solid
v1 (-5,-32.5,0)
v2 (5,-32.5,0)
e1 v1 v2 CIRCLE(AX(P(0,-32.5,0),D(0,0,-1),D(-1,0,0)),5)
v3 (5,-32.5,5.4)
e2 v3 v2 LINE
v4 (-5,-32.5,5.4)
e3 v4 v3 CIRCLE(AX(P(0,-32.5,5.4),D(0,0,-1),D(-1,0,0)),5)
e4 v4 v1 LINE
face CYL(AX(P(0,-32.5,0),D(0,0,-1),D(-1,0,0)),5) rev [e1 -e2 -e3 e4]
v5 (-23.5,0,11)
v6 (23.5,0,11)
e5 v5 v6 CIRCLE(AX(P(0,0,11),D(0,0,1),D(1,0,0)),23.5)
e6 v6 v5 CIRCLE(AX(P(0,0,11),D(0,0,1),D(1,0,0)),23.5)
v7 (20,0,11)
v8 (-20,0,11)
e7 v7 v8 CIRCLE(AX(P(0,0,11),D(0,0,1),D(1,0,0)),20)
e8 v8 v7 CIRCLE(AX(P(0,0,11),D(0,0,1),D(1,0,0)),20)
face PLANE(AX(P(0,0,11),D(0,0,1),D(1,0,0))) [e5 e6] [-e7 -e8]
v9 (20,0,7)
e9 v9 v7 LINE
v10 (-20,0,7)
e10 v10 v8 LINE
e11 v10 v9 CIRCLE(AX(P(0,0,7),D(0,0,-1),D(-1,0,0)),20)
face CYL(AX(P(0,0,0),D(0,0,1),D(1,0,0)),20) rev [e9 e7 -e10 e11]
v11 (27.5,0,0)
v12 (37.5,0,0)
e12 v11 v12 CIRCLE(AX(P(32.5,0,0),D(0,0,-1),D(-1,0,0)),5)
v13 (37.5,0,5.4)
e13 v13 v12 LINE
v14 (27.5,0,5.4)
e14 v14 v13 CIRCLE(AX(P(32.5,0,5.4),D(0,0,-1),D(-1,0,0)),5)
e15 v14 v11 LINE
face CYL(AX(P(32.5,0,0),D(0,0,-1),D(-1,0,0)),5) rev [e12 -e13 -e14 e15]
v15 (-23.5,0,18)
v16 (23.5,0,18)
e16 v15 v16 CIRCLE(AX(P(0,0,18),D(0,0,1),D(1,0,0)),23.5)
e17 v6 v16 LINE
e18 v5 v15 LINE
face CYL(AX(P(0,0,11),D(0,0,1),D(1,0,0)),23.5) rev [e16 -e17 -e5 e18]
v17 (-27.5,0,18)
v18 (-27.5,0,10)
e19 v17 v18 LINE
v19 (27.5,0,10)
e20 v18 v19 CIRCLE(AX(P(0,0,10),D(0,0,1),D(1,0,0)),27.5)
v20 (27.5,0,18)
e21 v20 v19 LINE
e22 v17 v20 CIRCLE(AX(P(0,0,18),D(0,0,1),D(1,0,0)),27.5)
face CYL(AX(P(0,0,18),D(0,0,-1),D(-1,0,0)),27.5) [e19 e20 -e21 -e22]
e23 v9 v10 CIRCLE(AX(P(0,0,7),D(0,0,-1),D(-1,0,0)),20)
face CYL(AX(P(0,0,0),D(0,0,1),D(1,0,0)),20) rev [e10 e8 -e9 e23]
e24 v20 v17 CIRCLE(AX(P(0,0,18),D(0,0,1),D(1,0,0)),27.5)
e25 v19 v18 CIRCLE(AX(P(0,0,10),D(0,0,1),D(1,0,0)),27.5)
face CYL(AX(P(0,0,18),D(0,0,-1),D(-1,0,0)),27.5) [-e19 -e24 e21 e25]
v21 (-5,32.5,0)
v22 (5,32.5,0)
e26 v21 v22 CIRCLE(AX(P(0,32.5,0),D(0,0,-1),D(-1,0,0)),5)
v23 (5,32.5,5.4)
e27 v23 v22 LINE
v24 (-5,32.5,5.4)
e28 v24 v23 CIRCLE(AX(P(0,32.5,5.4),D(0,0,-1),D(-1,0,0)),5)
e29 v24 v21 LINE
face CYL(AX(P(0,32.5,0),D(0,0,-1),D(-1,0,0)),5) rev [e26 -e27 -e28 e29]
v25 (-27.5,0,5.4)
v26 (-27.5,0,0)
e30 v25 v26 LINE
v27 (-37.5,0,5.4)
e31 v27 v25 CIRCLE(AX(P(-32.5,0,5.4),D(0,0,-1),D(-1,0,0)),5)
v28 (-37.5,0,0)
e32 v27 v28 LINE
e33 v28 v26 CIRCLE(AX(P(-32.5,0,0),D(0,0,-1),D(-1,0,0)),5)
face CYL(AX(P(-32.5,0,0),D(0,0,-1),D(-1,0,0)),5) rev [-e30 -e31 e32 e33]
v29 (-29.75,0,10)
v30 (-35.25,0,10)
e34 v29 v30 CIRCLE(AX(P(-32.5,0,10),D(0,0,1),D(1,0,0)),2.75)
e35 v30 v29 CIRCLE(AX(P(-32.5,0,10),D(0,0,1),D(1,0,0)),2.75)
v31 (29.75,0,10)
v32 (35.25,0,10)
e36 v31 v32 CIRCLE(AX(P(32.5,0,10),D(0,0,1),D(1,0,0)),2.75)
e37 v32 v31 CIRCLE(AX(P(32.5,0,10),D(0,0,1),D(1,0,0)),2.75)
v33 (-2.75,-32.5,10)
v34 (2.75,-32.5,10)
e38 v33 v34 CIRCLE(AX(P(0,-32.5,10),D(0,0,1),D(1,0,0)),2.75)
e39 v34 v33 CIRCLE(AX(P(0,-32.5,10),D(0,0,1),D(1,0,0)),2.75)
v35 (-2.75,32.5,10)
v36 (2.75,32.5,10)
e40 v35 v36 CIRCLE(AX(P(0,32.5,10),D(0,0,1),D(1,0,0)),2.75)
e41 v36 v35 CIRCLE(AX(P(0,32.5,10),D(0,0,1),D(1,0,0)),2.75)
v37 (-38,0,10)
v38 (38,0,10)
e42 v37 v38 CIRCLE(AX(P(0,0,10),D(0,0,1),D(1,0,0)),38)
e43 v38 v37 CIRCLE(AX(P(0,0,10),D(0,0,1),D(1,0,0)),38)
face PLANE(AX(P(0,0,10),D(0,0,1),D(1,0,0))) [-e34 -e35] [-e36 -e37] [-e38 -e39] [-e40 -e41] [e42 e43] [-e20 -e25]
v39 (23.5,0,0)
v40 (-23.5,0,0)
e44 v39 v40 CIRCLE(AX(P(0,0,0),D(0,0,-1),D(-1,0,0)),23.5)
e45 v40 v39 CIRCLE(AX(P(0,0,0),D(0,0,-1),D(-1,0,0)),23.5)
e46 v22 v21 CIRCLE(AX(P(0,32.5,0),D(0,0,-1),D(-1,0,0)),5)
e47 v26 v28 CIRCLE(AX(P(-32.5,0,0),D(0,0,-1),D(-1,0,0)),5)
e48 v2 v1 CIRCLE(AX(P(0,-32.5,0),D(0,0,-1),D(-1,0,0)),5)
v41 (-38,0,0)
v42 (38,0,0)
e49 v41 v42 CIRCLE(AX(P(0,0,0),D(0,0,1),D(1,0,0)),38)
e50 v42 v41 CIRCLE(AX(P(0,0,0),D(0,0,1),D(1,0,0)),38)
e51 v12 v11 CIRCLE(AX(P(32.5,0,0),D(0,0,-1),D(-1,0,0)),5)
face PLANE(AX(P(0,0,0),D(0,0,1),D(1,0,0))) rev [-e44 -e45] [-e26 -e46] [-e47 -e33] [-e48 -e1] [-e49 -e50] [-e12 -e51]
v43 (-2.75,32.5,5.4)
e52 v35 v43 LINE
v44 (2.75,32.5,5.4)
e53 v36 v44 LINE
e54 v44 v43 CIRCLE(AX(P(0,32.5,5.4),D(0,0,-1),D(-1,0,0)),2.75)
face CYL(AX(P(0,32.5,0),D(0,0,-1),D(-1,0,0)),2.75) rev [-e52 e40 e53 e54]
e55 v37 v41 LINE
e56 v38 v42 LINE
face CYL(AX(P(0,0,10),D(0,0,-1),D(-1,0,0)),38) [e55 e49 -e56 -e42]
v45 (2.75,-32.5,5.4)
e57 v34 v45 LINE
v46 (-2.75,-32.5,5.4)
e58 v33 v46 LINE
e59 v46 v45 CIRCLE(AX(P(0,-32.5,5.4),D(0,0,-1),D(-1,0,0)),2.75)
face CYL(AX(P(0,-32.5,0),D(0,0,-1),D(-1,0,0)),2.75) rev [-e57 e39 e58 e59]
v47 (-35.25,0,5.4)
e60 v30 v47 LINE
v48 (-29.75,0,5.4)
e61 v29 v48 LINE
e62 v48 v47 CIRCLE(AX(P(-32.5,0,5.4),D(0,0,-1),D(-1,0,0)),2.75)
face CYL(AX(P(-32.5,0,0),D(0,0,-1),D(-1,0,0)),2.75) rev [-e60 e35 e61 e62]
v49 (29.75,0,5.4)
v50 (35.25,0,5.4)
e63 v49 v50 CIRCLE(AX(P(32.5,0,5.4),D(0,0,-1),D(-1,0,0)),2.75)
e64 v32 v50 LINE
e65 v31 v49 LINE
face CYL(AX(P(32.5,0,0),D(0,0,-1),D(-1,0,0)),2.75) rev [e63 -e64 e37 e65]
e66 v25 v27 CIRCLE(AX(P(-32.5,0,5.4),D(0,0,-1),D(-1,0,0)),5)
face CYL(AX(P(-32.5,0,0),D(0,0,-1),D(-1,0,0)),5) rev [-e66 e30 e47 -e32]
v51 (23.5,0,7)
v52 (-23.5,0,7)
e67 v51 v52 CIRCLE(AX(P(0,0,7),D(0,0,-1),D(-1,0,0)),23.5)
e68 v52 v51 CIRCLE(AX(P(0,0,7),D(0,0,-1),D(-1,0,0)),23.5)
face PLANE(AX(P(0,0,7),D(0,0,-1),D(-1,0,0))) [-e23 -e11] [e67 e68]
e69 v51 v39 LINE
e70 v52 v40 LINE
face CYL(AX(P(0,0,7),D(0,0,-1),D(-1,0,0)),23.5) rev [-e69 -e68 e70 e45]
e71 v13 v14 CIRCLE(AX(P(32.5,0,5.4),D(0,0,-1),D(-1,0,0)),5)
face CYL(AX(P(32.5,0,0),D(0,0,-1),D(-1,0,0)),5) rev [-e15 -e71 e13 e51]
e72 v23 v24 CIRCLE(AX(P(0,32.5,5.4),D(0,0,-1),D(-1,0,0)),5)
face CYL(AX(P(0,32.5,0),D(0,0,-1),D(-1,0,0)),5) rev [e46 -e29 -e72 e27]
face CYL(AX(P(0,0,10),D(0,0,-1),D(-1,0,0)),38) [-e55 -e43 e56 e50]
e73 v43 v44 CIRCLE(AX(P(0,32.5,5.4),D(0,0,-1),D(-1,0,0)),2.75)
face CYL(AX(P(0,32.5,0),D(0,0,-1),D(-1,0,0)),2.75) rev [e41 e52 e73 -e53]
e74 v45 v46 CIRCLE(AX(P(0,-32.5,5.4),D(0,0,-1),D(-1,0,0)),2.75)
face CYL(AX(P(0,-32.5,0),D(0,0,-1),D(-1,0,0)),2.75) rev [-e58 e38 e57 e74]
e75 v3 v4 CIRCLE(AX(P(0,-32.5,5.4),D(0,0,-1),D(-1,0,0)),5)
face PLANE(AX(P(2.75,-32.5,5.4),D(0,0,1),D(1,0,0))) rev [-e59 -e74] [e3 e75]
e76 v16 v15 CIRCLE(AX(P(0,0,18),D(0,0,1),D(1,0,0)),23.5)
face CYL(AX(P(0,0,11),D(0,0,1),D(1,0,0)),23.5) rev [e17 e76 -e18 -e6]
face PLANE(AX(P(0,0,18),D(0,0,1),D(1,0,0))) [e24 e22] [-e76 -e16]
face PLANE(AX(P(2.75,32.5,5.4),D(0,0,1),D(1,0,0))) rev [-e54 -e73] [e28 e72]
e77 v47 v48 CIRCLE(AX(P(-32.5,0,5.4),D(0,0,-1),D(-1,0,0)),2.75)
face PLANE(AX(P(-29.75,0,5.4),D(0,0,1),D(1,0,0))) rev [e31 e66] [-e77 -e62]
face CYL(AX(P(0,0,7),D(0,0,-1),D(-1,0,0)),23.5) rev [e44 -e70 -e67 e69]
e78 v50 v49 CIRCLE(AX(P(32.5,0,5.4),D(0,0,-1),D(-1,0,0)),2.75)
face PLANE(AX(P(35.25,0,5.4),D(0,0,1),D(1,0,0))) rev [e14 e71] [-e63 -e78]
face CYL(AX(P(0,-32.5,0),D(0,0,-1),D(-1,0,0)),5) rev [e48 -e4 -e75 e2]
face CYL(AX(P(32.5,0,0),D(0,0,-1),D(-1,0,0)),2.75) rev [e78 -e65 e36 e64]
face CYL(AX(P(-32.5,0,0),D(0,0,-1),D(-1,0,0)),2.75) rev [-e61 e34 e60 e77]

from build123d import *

# Parameters (mm, degrees)
SKETCH1_R                                           = 38
BOSS_EXTRUDE1_DEPTH                                 = 10
SKETCH2_R                                           = 27.5
BOSS_EXTRUDE2_DEPTH                                 = 8
SKETCH3_R                                           = 23.5
CUT_EXTRUDE1_DEPTH                                  = 7
CUT_EXTRUDE2_START                                  = -7
SKETCH4_R                                           = 23.5
CUT_EXTRUDE2_DEPTH                                  = 7
SKETCH6_R                                           = 20
CUT_EXTRUDE3_DEPTH                                  = 57.674509261
CBORE_FOR_M5_HEX_SOCKET_HEAD_CAP_SCREW1_D           = 5.5
CBORE_FOR_M5_HEX_SOCKET_HEAD_CAP_SCREW1_CBORE_D     = 10
CBORE_FOR_M5_HEX_SOCKET_HEAD_CAP_SCREW1_CBORE_DEPTH = 5.4


with BuildPart() as part:
    # Sketch1 → Boss-Extrude1 (new body)
    with BuildSketch(Plane.XY):
        Circle(SKETCH1_R)
    extrude(amount=BOSS_EXTRUDE1_DEPTH)

    # Sketch2 → Boss-Extrude2 (add)
    with BuildSketch(Plane.XY.offset(10)):
        Circle(SKETCH2_R)
    extrude(amount=BOSS_EXTRUDE2_DEPTH)

    # Sketch3 → Cut-Extrude1 (cut)
    with BuildSketch(Plane.XY.offset(18)):
        Circle(SKETCH3_R)
    extrude(amount=-CUT_EXTRUDE1_DEPTH, mode=Mode.SUBTRACT)

    # Sketch4 → Cut-Extrude2 (cut)
    with BuildSketch(Plane(origin=(0, 0, 0), x_dir=(-1, 0, 0), z_dir=(0, 0, -1)).offset(CUT_EXTRUDE2_START)):
        with Locations(Location((0, 0, 0), (0, 0, 180))):
            Circle(SKETCH4_R)
    extrude(amount=CUT_EXTRUDE2_DEPTH, mode=Mode.SUBTRACT)

    # Sketch6 → Cut-Extrude3 (cut, through all)
    with BuildSketch(Plane.XY.offset(18)):
        Circle(SKETCH6_R)
    extrude(amount=-CUT_EXTRUDE3_DEPTH, mode=Mode.SUBTRACT)

    # CBORE for M5 Hex Socket Head Cap Screw1 (through all)
    with Locations(Plane(origin=(0, 0, 0), x_dir=(-1, 0, 0), z_dir=(0, 0, -1))):
        with Locations((0, 32.5), (-32.5, 0), (0, -32.5), (32.5, 0)):
            CounterBoreHole(CBORE_FOR_M5_HEX_SOCKET_HEAD_CAP_SCREW1_D / 2, CBORE_FOR_M5_HEX_SOCKET_HEAD_CAP_SCREW1_CBORE_D / 2, CBORE_FOR_M5_HEX_SOCKET_HEAD_CAP_SCREW1_CBORE_DEPTH)


solid = part.part
